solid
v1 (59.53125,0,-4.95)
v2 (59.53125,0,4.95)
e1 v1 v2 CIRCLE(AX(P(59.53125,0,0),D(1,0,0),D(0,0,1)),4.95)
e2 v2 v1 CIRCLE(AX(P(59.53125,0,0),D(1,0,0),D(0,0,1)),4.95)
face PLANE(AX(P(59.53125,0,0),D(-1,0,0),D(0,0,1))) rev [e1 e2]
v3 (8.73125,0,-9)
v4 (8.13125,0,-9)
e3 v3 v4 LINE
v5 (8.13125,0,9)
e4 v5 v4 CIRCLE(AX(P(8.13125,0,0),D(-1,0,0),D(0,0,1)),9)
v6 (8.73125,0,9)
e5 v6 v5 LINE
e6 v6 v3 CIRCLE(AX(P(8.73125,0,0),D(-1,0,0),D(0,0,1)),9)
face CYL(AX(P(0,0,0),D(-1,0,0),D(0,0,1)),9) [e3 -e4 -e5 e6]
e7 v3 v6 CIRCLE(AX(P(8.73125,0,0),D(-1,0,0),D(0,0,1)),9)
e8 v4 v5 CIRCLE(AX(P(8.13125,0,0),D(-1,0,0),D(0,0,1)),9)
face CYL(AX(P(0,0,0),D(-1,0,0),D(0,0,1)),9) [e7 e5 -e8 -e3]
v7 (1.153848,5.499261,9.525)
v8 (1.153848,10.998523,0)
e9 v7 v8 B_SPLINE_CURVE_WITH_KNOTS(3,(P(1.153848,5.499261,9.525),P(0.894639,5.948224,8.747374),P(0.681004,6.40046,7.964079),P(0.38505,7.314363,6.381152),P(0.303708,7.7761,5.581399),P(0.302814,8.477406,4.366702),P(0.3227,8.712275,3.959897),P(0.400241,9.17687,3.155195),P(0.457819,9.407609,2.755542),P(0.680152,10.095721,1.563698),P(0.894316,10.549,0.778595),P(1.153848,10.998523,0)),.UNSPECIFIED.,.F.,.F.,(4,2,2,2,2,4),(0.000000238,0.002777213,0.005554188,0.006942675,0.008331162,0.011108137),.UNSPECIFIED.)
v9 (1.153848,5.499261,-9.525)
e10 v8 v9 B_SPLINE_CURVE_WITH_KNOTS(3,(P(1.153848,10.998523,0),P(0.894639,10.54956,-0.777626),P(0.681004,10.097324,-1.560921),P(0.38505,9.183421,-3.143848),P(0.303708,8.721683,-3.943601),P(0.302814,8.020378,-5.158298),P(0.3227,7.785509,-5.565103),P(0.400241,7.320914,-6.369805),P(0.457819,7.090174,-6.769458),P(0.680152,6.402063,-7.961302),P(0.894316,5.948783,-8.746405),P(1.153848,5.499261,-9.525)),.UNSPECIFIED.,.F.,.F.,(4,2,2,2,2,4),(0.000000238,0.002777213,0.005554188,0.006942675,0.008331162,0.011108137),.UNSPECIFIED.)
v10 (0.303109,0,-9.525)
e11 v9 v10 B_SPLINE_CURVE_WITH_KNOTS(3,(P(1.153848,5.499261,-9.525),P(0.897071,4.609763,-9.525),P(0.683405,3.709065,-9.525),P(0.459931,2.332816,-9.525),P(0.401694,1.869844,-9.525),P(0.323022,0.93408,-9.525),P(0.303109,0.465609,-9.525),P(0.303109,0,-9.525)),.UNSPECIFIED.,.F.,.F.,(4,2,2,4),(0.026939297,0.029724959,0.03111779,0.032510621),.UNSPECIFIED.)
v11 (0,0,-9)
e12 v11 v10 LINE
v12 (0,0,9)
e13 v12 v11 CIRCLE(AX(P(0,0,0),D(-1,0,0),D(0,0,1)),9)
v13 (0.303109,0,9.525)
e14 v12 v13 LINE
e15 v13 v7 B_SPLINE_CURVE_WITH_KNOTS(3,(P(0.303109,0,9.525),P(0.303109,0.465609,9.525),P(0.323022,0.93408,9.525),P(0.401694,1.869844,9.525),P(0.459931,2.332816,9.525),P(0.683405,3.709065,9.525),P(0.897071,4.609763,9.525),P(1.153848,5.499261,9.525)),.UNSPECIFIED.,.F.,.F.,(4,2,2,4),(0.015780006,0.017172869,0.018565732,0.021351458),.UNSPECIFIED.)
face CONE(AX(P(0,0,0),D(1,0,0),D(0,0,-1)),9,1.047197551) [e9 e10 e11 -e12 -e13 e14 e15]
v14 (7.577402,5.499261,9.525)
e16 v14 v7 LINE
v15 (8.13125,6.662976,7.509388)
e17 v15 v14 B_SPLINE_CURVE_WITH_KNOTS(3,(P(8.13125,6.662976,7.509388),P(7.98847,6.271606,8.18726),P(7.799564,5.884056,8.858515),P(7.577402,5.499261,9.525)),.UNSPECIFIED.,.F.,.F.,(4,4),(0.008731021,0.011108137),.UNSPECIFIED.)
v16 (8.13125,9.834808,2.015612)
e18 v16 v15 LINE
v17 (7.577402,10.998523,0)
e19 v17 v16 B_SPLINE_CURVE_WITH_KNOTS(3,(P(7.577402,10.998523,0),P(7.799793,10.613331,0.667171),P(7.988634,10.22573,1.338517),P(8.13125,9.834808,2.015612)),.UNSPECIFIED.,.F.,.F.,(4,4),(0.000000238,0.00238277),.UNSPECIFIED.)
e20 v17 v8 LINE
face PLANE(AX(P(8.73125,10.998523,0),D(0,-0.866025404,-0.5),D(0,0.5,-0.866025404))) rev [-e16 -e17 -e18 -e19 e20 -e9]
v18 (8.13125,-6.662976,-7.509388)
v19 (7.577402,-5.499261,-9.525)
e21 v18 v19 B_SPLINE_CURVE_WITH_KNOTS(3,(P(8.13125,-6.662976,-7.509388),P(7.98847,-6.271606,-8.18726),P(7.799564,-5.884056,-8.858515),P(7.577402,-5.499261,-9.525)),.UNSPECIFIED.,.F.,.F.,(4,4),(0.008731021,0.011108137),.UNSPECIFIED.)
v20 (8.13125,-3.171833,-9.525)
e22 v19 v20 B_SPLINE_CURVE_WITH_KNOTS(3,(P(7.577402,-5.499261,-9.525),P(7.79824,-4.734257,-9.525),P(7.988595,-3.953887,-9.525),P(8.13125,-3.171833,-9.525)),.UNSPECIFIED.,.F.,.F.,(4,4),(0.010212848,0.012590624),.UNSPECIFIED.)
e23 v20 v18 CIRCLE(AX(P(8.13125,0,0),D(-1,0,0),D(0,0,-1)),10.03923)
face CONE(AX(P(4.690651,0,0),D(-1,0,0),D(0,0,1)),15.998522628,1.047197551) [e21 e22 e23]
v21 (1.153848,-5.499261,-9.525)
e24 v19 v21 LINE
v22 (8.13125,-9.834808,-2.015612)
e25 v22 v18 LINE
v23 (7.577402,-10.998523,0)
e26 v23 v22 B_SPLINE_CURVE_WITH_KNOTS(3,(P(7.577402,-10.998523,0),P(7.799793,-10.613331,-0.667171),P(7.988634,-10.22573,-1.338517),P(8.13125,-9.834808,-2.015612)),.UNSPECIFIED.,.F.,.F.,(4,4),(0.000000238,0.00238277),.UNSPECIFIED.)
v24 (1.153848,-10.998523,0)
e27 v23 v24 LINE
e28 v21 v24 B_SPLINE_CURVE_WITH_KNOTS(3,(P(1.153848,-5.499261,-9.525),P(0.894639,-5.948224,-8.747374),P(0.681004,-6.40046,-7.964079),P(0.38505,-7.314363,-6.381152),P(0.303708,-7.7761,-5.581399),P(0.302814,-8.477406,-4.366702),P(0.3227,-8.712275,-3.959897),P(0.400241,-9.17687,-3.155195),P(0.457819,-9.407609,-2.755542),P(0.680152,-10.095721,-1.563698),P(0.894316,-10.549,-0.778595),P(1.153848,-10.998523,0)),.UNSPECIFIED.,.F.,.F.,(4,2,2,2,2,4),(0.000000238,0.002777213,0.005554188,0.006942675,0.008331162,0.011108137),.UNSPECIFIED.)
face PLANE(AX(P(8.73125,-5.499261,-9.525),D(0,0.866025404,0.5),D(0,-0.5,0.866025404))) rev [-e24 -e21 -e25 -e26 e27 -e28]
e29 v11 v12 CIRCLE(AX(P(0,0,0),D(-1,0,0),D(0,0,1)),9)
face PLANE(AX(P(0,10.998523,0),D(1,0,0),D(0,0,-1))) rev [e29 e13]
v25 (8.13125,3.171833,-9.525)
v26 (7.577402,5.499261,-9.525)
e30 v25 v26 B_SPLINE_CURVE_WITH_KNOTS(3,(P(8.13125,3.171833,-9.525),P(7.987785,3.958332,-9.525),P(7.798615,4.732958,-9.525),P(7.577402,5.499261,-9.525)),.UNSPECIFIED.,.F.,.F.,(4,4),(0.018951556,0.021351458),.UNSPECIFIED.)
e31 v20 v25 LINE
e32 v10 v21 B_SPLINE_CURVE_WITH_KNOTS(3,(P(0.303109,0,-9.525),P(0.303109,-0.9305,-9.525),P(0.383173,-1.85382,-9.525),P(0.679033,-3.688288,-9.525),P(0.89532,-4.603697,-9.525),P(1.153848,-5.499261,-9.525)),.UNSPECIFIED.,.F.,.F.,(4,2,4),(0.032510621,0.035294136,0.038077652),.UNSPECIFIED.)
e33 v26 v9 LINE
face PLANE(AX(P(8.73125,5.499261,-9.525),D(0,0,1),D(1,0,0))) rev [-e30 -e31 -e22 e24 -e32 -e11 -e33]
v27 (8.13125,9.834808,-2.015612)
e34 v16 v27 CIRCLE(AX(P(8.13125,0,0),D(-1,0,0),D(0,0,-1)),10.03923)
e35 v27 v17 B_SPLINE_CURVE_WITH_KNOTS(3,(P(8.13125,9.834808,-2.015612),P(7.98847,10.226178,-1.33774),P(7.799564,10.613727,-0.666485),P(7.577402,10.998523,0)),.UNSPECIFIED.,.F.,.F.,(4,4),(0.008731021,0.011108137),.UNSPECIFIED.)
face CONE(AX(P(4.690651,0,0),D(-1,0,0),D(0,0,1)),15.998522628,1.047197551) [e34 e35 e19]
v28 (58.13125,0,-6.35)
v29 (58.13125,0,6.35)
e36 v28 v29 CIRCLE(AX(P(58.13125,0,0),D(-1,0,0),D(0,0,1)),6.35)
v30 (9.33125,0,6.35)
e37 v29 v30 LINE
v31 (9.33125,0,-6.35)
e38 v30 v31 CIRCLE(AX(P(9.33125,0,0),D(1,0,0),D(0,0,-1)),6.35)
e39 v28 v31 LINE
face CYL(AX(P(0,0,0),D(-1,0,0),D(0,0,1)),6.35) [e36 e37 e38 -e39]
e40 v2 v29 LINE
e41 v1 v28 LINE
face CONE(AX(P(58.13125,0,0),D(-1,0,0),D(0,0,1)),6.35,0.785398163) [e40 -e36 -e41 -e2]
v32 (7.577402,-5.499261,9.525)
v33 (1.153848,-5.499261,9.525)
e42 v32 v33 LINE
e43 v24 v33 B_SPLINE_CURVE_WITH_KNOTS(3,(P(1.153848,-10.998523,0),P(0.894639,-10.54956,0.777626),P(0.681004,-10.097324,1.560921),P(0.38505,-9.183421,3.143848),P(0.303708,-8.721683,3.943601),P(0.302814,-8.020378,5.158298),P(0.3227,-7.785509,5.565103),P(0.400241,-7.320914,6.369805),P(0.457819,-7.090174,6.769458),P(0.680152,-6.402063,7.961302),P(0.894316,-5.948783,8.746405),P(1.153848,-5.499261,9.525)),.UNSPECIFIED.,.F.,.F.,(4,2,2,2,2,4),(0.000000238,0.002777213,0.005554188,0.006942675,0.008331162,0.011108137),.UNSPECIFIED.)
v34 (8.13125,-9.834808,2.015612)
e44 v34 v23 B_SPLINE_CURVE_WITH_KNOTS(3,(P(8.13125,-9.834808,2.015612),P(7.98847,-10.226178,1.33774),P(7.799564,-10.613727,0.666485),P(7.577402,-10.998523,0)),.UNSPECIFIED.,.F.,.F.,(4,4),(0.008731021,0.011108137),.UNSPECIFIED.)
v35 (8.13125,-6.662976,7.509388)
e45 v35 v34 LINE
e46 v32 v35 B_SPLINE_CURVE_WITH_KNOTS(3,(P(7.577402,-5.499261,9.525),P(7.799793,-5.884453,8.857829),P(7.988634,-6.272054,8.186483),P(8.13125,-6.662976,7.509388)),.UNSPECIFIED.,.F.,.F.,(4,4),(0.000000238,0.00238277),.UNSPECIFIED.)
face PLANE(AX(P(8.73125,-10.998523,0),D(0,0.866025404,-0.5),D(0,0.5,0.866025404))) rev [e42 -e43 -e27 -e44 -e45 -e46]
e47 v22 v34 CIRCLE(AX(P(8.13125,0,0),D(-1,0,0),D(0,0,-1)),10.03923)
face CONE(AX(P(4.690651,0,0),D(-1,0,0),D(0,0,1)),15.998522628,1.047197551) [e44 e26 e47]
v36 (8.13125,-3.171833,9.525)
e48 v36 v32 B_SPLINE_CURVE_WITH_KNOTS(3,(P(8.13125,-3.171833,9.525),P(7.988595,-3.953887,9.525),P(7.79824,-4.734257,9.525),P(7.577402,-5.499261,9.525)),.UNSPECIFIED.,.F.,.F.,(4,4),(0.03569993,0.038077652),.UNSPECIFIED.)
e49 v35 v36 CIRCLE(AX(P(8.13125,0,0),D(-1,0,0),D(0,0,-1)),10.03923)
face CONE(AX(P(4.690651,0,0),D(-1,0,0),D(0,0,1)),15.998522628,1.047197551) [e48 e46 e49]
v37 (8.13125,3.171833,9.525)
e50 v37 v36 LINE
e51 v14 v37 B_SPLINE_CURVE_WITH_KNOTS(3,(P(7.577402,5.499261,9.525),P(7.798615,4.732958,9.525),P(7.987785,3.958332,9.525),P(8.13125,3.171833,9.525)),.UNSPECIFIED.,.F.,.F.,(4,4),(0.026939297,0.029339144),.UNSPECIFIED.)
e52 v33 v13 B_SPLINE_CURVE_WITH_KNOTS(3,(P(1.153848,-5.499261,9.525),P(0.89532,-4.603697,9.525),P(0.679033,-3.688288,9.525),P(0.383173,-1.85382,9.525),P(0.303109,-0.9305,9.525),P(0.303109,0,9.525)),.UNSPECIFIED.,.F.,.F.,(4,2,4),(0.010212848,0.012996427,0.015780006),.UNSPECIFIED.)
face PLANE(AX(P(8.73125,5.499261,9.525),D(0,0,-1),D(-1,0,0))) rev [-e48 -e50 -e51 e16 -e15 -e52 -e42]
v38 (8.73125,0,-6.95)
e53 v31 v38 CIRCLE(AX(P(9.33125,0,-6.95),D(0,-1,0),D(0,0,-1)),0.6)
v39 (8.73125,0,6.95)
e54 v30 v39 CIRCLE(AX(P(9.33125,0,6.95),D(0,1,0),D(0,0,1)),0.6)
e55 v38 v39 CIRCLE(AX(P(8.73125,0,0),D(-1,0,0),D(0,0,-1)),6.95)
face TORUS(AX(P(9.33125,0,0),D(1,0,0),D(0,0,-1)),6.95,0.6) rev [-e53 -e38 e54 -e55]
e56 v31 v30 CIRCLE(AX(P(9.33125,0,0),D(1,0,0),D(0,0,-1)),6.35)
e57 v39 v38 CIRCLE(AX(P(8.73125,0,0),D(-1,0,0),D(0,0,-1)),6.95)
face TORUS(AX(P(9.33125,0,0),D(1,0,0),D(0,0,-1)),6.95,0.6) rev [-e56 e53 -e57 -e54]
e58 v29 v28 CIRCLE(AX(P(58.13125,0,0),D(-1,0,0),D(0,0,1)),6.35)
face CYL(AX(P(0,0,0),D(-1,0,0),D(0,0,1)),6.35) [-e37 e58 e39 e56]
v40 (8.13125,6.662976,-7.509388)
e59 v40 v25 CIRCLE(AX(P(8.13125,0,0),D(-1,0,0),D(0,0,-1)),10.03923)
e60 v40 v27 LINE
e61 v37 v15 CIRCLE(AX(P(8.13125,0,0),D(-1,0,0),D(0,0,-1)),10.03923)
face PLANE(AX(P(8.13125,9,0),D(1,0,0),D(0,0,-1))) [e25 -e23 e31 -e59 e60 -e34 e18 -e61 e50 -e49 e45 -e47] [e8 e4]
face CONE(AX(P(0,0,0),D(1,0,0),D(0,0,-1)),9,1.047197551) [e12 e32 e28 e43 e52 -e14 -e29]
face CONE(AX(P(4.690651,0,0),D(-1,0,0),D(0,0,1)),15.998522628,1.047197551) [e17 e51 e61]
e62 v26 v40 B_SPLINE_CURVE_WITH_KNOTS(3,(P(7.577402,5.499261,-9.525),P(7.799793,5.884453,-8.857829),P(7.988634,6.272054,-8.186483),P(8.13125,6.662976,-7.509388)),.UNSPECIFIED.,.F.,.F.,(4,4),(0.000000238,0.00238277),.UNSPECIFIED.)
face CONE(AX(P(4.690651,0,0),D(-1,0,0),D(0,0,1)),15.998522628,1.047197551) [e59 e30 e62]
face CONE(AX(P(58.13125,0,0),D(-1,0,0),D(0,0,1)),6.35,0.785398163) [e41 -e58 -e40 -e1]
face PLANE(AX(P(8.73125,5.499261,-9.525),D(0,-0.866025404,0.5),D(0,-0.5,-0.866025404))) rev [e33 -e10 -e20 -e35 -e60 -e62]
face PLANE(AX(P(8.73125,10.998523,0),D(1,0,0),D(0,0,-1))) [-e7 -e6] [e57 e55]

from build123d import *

# Parameters (mm, degrees)
BASE_EXTRUDE_DEPTH = 8.73125
SKETCH4_W          = 0.6
SKETCH4_H          = 11.998522628
CHAMFER_2_SIZE     = 1.4
FILLET_2_R         = 0.6


with BuildPart() as part:
    # Sketch1 → Base-Extrude (new body)
    with BuildSketch(Plane(origin=(0, 0, 0), x_dir=(0, 0, -1), z_dir=(1, 0, 0))):
        Polygon((9.525, 5.499261314), (9.525, -5.499261314), (0, -10.998522628), (-9.525, -5.499261314), (-9.525, 5.499261314), (0, 10.998522628), align=None)
    extrude(amount=BASE_EXTRUDE_DEPTH)

    # Sketch2 → Boss-Revolve1 (revolve)
    with BuildSketch(Plane.XY, mode=Mode.PRIVATE) as boss_revolve1_sk:
        Polygon((0, 0), (59.53125, 0), (59.53125, 5.55625), (59.53125, 6.35), (27.8072, 6.35), (0, 6.35), align=None)
    revolve(boss_revolve1_sk.sketch.rotate(Axis((0, 0, 0), (1, 0, 0)), 90), axis=Axis((0, 0, 0), (1, 0, 0)))

    # Sketch3 → Cut-Revolve1 (revolve, cut)
    with BuildSketch(Plane.XY, mode=Mode.PRIVATE) as cut_revolve1_sk:
        Polygon((0, 9), (4.040598923, 15.998522628), (4.040598923, 20.998522628), (-10, 20.998522628), (-10, 9), align=None)
    revolve(cut_revolve1_sk.sketch.rotate(Axis((0, 0, 0), (1, 0, 0)), 300.000000006), axis=Axis((0, 0, 0), (1, 0, 0)), mode=Mode.SUBTRACT)

    # Sketch5 → Cut-Revolve2 (revolve, cut)
    with BuildSketch(Plane.XY, mode=Mode.PRIVATE) as cut_revolve2_sk:
        Polygon((8.73125, 9), (4.690651077, 15.998522628), (4.690651077, 20.998522628), (14.690651077, 20.998522628), (14.690651077, 9), align=None)
    revolve(cut_revolve2_sk.sketch.rotate(Axis((0, 0, 0), (1, 0, 0)), 90), axis=Axis((0, 0, 0), (1, 0, 0)), mode=Mode.SUBTRACT)

    # Sketch4 → Cut-Revolve3 (revolve, cut)
    with BuildSketch(Plane.XY, mode=Mode.PRIVATE) as cut_revolve3_sk:
        with Locations((8.43125, 14.999261314)):
            Rectangle(SKETCH4_W, SKETCH4_H)
    revolve(cut_revolve3_sk.sketch.rotate(Axis((0, 0, 0), (1, 0, 0)), 90), axis=Axis((0, 0, 0), (1, 0, 0)), mode=Mode.SUBTRACT)

    # Chamfer 2
    chamfer_2_edges = [part.edges().sort_by_distance(p)[0] for p in [
        (59.53125, 0, -6.35),
    ]]
    chamfer(chamfer_2_edges, length=CHAMFER_2_SIZE)

    # Fillet 2
    fillet_2_edges = [part.edges().sort_by_distance(p)[0] for p in [
        (8.73125, 0, -6.35),
    ]]
    fillet(fillet_2_edges, radius=FILLET_2_R)


solid = part.part
